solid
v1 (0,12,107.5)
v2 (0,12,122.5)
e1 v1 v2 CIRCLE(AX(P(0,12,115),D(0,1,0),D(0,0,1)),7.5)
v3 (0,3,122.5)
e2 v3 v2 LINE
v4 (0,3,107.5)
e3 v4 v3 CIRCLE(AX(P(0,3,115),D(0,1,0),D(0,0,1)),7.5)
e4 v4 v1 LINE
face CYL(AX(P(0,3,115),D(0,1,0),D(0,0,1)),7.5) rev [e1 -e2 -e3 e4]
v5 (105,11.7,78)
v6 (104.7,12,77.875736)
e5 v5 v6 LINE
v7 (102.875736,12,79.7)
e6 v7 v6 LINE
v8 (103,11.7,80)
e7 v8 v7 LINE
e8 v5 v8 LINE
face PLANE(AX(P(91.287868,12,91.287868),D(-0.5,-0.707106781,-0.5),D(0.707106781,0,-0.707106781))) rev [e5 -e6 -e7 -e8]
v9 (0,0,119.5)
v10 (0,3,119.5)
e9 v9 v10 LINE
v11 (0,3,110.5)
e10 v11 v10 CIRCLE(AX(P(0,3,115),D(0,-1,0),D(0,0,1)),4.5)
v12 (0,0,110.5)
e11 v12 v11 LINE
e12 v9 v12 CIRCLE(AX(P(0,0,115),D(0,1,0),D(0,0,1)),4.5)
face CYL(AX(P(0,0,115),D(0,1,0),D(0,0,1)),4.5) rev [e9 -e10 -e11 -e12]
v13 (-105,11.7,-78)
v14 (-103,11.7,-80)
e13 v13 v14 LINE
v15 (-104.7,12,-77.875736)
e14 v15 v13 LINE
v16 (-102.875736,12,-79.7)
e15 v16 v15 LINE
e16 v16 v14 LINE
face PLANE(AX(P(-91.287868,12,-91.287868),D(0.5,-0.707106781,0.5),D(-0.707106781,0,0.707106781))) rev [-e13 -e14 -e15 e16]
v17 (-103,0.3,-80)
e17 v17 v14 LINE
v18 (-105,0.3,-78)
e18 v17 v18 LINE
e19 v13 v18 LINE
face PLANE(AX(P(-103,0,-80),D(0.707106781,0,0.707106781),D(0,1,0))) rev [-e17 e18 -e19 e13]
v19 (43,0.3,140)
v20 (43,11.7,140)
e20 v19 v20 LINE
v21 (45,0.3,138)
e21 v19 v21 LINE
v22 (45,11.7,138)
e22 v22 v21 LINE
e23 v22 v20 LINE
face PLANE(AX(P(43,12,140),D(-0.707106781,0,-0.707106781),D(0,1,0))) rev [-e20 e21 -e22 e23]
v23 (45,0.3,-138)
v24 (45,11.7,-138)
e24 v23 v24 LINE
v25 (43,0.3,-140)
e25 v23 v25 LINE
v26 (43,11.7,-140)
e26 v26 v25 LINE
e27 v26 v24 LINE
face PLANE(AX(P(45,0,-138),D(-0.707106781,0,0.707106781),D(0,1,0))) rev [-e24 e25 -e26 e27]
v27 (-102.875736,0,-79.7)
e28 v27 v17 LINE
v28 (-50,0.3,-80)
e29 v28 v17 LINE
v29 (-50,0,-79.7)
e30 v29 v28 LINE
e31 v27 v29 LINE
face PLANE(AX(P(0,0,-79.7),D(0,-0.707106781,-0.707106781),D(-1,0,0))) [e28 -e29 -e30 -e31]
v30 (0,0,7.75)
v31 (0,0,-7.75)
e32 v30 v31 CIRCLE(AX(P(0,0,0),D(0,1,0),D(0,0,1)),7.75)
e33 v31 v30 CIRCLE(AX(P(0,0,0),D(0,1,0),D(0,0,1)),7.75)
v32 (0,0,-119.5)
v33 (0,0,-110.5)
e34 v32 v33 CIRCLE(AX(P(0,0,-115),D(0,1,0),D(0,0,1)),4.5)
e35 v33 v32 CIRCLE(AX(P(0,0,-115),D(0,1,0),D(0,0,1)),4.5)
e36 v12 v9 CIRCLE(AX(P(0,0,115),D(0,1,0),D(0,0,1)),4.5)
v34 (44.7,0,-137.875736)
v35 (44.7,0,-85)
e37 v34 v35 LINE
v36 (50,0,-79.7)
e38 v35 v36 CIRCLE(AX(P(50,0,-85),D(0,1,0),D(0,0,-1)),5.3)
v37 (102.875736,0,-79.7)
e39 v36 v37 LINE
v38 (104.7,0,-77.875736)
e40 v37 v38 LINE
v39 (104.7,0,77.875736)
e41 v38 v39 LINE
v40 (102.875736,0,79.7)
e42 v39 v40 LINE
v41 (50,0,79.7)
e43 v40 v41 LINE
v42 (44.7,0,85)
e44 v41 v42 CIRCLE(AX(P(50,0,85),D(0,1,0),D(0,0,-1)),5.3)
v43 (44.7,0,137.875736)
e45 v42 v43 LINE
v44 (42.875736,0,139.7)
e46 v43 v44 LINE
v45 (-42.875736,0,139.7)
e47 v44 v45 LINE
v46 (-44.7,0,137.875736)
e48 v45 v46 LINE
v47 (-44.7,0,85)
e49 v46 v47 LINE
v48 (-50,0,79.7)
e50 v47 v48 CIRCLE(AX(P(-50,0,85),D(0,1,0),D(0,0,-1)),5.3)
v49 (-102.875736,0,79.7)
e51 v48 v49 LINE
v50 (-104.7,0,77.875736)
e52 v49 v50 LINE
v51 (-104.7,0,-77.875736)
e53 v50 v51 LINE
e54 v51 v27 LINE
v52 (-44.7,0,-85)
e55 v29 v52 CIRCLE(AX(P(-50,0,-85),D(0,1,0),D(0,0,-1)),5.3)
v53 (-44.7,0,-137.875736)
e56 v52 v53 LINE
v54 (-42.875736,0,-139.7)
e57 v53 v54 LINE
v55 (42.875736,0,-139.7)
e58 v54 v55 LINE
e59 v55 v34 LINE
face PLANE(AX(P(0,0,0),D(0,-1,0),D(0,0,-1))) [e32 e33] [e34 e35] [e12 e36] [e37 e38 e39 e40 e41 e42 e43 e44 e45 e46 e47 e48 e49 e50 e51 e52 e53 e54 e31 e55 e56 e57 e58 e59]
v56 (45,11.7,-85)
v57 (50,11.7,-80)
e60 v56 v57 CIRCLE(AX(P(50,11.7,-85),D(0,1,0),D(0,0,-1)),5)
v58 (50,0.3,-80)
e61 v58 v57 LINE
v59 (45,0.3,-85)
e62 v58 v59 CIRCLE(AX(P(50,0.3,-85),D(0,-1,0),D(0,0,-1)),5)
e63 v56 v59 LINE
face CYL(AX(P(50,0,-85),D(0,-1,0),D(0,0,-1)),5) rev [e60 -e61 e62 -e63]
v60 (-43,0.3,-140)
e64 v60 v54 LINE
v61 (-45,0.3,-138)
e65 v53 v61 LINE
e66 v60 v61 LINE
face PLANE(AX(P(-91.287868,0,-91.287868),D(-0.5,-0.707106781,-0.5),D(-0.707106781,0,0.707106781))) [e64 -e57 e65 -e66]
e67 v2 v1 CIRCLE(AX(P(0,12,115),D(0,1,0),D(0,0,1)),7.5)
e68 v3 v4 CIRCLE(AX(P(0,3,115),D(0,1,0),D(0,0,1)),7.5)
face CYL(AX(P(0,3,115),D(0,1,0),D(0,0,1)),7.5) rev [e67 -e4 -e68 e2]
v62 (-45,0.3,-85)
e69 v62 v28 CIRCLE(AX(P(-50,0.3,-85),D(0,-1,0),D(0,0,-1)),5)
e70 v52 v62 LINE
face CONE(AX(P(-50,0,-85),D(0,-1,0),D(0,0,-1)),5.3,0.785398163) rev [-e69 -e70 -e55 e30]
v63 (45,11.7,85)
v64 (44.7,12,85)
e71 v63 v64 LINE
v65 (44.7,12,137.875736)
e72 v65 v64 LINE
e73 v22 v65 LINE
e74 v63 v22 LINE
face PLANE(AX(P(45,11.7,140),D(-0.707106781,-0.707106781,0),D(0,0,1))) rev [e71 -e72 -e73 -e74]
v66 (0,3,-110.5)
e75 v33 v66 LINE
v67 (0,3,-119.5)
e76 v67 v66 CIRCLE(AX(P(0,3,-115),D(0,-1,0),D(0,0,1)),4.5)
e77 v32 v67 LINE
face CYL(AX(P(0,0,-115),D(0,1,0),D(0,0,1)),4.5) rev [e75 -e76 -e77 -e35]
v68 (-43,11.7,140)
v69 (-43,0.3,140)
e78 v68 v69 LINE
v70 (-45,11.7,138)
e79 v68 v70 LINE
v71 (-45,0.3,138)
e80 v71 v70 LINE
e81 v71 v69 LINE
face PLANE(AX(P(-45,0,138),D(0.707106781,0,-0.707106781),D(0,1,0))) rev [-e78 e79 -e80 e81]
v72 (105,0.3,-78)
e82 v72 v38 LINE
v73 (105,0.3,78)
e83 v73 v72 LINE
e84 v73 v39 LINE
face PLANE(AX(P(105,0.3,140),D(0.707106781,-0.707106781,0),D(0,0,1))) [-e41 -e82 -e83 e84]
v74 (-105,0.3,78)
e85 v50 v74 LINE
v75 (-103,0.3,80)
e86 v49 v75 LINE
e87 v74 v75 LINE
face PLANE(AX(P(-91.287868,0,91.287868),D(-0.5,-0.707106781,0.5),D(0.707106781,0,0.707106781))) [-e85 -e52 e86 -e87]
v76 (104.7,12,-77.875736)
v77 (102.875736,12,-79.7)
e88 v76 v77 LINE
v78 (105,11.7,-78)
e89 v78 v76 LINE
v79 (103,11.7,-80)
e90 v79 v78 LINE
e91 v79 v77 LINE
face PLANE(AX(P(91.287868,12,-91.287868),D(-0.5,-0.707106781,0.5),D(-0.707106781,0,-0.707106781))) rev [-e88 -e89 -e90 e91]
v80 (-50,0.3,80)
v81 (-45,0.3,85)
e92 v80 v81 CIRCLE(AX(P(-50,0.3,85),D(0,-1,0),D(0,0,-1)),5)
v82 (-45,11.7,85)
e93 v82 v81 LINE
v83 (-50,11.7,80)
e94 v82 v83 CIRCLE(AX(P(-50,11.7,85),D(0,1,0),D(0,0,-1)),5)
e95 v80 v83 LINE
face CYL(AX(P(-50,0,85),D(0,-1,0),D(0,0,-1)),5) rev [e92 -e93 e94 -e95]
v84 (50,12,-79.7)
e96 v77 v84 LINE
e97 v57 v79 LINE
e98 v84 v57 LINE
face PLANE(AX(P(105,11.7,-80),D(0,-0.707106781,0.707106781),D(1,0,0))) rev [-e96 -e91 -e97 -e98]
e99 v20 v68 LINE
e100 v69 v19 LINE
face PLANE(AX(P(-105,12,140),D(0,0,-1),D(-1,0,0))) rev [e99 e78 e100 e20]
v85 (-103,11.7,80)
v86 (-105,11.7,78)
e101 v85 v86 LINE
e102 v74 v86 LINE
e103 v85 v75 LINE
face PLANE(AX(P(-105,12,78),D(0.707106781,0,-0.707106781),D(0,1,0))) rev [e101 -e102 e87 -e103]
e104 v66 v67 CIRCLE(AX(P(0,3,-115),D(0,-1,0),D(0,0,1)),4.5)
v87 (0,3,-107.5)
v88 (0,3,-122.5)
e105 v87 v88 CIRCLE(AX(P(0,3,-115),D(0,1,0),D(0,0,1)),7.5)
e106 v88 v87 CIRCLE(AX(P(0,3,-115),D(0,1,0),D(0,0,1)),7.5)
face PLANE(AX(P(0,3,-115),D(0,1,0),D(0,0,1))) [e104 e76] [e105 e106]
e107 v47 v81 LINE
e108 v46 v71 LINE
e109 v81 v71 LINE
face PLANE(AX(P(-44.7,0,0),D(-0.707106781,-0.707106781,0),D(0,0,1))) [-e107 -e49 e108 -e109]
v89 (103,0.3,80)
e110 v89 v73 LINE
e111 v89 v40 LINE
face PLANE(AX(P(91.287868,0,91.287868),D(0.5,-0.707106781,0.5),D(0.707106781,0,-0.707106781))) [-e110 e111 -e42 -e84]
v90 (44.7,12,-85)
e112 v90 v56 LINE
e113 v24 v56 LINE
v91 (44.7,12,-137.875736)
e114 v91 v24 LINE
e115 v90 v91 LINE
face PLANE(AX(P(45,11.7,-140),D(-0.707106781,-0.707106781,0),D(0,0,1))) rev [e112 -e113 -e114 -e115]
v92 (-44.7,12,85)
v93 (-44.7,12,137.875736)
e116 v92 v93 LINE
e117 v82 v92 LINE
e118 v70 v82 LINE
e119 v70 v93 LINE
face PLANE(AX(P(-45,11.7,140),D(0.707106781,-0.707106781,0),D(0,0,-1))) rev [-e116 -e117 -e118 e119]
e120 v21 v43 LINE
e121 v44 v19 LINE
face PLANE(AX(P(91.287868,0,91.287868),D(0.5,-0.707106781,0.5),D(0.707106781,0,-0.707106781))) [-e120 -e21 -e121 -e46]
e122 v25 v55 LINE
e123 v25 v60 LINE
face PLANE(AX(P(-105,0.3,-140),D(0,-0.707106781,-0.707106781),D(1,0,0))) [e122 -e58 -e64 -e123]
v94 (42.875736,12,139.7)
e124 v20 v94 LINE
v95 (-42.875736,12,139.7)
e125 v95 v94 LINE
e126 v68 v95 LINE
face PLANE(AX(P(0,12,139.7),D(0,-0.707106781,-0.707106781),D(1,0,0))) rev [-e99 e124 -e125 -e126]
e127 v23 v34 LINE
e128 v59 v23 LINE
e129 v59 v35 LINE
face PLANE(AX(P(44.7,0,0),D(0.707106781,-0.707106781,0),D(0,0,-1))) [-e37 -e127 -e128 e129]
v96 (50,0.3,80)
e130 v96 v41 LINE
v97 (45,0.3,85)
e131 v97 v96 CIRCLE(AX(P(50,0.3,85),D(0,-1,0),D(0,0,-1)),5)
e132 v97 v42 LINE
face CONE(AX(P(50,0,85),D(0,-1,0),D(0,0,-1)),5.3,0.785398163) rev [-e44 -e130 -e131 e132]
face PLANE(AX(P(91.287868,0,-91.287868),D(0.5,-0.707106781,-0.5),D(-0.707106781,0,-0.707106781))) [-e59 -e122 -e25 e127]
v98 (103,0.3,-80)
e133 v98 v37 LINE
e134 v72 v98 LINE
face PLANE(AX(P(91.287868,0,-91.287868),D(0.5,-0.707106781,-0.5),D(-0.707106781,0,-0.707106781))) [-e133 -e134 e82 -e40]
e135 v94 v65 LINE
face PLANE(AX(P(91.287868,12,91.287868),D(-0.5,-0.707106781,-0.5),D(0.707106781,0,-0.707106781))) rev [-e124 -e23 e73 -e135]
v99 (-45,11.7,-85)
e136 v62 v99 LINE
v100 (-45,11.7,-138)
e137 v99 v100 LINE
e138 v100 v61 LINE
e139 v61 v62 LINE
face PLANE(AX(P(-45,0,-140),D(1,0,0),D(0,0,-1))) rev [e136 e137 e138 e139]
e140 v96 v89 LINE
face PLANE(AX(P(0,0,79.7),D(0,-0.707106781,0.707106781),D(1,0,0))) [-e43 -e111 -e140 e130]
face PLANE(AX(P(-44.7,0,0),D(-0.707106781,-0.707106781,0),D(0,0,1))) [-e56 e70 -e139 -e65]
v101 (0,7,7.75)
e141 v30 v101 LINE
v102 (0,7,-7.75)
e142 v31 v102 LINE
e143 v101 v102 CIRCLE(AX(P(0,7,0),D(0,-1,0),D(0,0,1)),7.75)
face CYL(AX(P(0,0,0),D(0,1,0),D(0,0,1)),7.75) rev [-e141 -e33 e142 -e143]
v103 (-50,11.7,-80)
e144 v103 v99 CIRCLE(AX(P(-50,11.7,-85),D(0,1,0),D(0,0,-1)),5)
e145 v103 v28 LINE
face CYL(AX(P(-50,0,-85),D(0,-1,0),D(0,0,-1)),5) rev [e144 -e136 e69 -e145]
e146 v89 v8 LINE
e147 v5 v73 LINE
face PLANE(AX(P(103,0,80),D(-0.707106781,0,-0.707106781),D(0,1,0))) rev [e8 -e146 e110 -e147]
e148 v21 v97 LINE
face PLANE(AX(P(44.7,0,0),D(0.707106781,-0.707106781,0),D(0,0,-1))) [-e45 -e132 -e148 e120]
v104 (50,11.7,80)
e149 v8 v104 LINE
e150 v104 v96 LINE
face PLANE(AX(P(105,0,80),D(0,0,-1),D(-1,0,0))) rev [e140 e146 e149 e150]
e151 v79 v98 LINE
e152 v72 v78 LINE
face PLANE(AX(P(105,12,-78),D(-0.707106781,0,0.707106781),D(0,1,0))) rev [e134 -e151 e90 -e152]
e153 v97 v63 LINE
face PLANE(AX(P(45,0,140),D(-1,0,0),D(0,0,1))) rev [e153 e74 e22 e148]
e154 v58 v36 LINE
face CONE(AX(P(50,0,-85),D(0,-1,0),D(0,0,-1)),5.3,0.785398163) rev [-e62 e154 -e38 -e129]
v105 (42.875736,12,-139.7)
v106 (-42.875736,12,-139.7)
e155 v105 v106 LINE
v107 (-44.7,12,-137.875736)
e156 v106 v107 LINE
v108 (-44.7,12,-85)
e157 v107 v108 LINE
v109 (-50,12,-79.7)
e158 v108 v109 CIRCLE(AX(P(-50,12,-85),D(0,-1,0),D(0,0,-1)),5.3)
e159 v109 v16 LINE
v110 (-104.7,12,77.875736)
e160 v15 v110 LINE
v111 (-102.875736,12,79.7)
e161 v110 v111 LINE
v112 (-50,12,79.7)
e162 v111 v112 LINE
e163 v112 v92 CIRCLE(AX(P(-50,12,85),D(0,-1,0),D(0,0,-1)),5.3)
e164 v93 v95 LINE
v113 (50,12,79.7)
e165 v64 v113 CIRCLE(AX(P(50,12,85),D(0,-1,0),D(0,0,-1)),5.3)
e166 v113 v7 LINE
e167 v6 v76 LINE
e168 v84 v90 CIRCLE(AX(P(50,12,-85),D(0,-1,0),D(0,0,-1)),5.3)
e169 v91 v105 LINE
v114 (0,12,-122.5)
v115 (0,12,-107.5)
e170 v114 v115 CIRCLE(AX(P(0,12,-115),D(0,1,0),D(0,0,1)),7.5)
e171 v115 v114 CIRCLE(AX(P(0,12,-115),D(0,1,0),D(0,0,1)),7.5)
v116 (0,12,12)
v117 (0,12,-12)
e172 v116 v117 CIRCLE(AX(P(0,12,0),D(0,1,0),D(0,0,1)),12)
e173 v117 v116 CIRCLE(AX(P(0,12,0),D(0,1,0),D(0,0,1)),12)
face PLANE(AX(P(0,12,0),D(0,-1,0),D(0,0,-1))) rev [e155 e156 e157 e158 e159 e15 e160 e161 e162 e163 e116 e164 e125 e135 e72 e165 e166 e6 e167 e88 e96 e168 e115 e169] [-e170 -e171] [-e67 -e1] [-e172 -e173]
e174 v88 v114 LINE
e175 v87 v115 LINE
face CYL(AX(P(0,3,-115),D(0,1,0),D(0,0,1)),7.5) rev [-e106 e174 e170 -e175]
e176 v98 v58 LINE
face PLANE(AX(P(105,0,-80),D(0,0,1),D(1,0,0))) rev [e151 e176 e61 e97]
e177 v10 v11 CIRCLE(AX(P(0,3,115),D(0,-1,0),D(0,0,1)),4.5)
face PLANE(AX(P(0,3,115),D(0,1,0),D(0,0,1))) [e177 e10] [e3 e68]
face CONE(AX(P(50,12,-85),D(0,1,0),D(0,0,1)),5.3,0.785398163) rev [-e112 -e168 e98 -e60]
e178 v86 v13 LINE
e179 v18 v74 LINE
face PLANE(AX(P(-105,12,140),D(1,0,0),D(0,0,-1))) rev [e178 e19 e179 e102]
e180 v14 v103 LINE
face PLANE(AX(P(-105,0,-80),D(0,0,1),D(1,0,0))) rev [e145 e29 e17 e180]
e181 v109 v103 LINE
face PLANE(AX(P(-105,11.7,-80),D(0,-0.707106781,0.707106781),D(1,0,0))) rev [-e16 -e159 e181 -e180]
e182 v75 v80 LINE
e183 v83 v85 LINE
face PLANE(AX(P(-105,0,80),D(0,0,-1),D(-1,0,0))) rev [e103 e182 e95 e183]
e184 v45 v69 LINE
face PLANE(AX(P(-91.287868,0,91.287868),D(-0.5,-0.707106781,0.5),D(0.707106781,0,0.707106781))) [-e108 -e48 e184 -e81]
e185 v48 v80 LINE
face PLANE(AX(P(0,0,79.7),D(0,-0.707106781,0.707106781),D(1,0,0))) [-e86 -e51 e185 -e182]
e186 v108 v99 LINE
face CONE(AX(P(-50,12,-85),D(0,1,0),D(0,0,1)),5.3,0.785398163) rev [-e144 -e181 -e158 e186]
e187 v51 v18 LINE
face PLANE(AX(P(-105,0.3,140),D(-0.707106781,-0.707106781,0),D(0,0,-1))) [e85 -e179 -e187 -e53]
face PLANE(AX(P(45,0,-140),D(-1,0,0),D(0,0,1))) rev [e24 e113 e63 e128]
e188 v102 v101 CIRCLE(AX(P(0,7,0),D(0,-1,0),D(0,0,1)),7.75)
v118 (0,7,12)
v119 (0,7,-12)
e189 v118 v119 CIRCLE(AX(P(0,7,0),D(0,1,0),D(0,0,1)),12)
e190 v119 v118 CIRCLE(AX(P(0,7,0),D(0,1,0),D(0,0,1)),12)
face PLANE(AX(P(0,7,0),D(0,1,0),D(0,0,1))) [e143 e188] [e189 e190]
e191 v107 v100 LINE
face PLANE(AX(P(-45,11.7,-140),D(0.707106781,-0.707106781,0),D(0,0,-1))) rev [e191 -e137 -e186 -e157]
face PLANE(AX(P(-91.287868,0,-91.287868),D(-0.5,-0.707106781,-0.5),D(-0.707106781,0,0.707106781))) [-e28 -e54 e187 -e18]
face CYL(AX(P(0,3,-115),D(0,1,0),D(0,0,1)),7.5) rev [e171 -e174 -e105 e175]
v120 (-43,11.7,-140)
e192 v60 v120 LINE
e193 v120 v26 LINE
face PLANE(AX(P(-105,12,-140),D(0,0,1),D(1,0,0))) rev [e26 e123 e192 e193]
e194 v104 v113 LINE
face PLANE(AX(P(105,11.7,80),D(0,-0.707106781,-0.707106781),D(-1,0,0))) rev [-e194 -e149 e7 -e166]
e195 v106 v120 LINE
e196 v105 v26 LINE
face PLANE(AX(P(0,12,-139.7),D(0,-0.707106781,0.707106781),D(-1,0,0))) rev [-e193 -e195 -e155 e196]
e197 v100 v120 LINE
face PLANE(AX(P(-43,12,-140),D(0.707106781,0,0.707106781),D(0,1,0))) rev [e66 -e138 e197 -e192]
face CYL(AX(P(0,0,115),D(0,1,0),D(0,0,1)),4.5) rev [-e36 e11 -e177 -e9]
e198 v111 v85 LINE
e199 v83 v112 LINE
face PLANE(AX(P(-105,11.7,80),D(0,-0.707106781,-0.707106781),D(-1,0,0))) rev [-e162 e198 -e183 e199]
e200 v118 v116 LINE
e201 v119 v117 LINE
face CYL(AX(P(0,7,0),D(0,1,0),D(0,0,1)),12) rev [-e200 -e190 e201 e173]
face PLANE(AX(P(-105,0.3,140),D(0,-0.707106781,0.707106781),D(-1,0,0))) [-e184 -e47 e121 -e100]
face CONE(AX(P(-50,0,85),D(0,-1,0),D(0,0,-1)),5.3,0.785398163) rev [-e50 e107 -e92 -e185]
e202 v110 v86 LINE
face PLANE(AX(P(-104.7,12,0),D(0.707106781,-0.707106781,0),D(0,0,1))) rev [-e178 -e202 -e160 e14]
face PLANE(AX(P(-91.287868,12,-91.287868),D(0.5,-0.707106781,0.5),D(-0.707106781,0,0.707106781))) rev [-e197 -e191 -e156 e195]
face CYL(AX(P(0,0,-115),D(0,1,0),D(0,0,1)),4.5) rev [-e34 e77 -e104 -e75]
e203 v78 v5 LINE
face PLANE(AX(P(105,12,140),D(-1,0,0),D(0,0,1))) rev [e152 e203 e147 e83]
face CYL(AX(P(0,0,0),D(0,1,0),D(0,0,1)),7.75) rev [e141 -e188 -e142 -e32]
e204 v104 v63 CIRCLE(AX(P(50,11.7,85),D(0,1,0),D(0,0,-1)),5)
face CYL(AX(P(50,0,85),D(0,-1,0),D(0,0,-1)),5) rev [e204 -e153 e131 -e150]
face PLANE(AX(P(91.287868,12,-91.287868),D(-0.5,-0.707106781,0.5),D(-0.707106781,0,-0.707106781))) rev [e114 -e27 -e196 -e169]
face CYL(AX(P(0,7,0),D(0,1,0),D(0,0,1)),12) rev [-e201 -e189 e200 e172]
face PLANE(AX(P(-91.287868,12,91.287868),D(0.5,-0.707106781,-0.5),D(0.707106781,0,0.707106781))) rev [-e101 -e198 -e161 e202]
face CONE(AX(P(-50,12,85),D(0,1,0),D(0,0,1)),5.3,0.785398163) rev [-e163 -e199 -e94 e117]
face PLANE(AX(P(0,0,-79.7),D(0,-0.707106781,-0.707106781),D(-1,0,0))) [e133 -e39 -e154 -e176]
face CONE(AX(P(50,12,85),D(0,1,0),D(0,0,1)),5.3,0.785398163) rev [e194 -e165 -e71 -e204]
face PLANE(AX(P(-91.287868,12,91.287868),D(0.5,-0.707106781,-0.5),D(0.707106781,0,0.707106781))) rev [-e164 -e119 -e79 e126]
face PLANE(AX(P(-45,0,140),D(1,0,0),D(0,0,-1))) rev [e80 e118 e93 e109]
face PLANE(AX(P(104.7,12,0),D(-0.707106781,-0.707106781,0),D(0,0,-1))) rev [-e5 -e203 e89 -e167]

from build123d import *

# Parameters (mm, degrees)
SKETCH_1_W          = 210
SKETCH_1_H          = 280
EXTRUDE_1_DEPTH     = 12
SKETCH_2_R          = 7.75
SKETCH_2_R_2        = 4.5
CUT_EXTRUDE_1_DEPTH = 176.410946067
SKETCH_3_W          = 60
SKETCH_3_H          = 60
CUT_EXTRUDE_2_DEPTH = 176.410946067
FILLET_1_R          = 5
CHAMFER_1_SIZE      = 2
SKETCH_4_R          = 7.5
CUT_EXTRUDE_3_DEPTH = 9
SKETCH_5_R          = 12
CUT_EXTRUDE_4_DEPTH = 5
CHAMFER_2_SIZE      = 0.3
CHAMFER_3_SIZE      = 0.3


with BuildPart() as part:
    # 草图1 → 凸台-拉伸1 (new body)
    with BuildSketch(Plane(origin=(0, 0, 0), x_dir=(1, 0, 0), z_dir=(0, 1, 0))):
        Rectangle(SKETCH_1_W, SKETCH_1_H)
    extrude(amount=EXTRUDE_1_DEPTH)

    # 草图2 → 切除-拉伸1 (cut, through all)
    with BuildSketch(Plane(origin=(0, 12, 0), x_dir=(1, 0, 0), z_dir=(0, 1, 0))):
        with Locations(Location((0, 0, 0), (0, 0, 270))):
            Circle(SKETCH_2_R)
        with Locations(Location((0, -115, 0), (0, 0, 270))):
            Circle(SKETCH_2_R_2)
        with Locations(Location((0, 115, 0), (0, 0, 270))):
            Circle(SKETCH_2_R_2)
    extrude(amount=-CUT_EXTRUDE_1_DEPTH, mode=Mode.SUBTRACT)

    # 草图3 → 切除-拉伸2 (cut, through all)
    with BuildSketch(Plane(origin=(0, 12, 0), x_dir=(1, 0, 0), z_dir=(0, 1, 0))):
        with Locations((-75, -110)):
            Rectangle(SKETCH_3_W, SKETCH_3_H)
        with Locations((-75, 110)):
            Rectangle(SKETCH_3_W, SKETCH_3_H)
        with Locations((75, 110)):
            Rectangle(SKETCH_3_W, SKETCH_3_H)
        with Locations((75, -110)):
            Rectangle(SKETCH_3_W, SKETCH_3_H)
    extrude(amount=-CUT_EXTRUDE_2_DEPTH, mode=Mode.SUBTRACT)

    # 圆角1
    fillet_1_edges = [part.edges().sort_by_distance(p)[0] for p in [
        (-45, 6, 80),
        (-45, 6, -80),
        (45, 6, -80),
        (45, 6, 80),
    ]]
    fillet(fillet_1_edges, radius=FILLET_1_R)

    # 倒角1
    chamfer_1_edges = [part.edges().sort_by_distance(p)[0] for p in [
        (-105, 6, 80),
        (-45, 6, 140),
        (-105, 6, -80),
        (-45, 6, -140),
        (105, 6, -80),
        (45, 6, -140),
        (105, 6, 80),
        (45, 6, 140),
    ]]
    chamfer(chamfer_1_edges, length=CHAMFER_1_SIZE)

    # 草图4 → 切除-拉伸3 (cut)
    with BuildSketch(Plane(origin=(0, 12, 0), x_dir=(1, 0, 0), z_dir=(0, 1, 0))):
        with Locations(Location((0, -115, 0), (0, 0, 270))):
            Circle(SKETCH_4_R)
        with Locations(Location((0, 115, 0), (0, 0, 270))):
            Circle(SKETCH_4_R)
    extrude(amount=-CUT_EXTRUDE_3_DEPTH, mode=Mode.SUBTRACT)

    # 草图5 → 切除-拉伸4 (cut)
    with BuildSketch(Plane(origin=(0, 12, 0), x_dir=(1, 0, 0), z_dir=(0, 1, 0))):
        with Locations(Location((0, 0, 0), (0, 0, 270))):
            Circle(SKETCH_5_R)
    extrude(amount=-CUT_EXTRUDE_4_DEPTH, mode=Mode.SUBTRACT)

    # 倒角2
    chamfer_2_edges = [part.edges().sort_by_distance(p)[0] for p in [
        (76.5, 12, 80),
        (0, 12, 140),
        (105, 12, 0),
        (45, 12, -111.5),
        (0, 12, -140),
        (-76.5, 12, -80),
        (-105, 12, 0),
        (-45, 12, 111.5),
        (44, 12, -139),
        (104, 12, -79),
        (-44, 12, -139),
        (-104, 12, -79),
        (-104, 12, 79),
        (-44, 12, 139),
        (44, 12, 139),
        (104, 12, 79),
        (-45, 12, -111.5),
        (76.5, 12, -80),
        (45, 12, 111.5),
        (-76.5, 12, 80),
        (-46.464466094, 12, -81.464466094),
        (46.464466094, 12, -81.464466094),
        (46.464466094, 12, 81.464466094),
        (-46.464466094, 12, 81.464466094),
    ]]
    chamfer(chamfer_2_edges, length=CHAMFER_2_SIZE)

    # 倒角3
    chamfer_3_edges = [part.edges().sort_by_distance(p)[0] for p in [
        (76.5, 0, 80),
        (105, 0, 0),
        (0, 0, 140),
        (-45, 0, 111.5),
        (-105, 0, 0),
        (-76.5, 0, -80),
        (0, 0, -140),
        (45, 0, -111.5),
        (44, 0, -139),
        (104, 0, -79),
        (-44, 0, -139),
        (-104, 0, -79),
        (-104, 0, 79),
        (-44, 0, 139),
        (44, 0, 139),
        (104, 0, 79),
        (-45, 0, -111.5),
        (76.5, 0, -80),
        (45, 0, 111.5),
        (-76.5, 0, 80),
        (-46.464466094, 0, -81.464466094),
        (46.464466094, 0, -81.464466094),
        (46.464466094, 0, 81.464466094),
        (-46.464466094, 0, 81.464466094),
    ]]
    chamfer(chamfer_3_edges, length=CHAMFER_3_SIZE)


solid = part.part
